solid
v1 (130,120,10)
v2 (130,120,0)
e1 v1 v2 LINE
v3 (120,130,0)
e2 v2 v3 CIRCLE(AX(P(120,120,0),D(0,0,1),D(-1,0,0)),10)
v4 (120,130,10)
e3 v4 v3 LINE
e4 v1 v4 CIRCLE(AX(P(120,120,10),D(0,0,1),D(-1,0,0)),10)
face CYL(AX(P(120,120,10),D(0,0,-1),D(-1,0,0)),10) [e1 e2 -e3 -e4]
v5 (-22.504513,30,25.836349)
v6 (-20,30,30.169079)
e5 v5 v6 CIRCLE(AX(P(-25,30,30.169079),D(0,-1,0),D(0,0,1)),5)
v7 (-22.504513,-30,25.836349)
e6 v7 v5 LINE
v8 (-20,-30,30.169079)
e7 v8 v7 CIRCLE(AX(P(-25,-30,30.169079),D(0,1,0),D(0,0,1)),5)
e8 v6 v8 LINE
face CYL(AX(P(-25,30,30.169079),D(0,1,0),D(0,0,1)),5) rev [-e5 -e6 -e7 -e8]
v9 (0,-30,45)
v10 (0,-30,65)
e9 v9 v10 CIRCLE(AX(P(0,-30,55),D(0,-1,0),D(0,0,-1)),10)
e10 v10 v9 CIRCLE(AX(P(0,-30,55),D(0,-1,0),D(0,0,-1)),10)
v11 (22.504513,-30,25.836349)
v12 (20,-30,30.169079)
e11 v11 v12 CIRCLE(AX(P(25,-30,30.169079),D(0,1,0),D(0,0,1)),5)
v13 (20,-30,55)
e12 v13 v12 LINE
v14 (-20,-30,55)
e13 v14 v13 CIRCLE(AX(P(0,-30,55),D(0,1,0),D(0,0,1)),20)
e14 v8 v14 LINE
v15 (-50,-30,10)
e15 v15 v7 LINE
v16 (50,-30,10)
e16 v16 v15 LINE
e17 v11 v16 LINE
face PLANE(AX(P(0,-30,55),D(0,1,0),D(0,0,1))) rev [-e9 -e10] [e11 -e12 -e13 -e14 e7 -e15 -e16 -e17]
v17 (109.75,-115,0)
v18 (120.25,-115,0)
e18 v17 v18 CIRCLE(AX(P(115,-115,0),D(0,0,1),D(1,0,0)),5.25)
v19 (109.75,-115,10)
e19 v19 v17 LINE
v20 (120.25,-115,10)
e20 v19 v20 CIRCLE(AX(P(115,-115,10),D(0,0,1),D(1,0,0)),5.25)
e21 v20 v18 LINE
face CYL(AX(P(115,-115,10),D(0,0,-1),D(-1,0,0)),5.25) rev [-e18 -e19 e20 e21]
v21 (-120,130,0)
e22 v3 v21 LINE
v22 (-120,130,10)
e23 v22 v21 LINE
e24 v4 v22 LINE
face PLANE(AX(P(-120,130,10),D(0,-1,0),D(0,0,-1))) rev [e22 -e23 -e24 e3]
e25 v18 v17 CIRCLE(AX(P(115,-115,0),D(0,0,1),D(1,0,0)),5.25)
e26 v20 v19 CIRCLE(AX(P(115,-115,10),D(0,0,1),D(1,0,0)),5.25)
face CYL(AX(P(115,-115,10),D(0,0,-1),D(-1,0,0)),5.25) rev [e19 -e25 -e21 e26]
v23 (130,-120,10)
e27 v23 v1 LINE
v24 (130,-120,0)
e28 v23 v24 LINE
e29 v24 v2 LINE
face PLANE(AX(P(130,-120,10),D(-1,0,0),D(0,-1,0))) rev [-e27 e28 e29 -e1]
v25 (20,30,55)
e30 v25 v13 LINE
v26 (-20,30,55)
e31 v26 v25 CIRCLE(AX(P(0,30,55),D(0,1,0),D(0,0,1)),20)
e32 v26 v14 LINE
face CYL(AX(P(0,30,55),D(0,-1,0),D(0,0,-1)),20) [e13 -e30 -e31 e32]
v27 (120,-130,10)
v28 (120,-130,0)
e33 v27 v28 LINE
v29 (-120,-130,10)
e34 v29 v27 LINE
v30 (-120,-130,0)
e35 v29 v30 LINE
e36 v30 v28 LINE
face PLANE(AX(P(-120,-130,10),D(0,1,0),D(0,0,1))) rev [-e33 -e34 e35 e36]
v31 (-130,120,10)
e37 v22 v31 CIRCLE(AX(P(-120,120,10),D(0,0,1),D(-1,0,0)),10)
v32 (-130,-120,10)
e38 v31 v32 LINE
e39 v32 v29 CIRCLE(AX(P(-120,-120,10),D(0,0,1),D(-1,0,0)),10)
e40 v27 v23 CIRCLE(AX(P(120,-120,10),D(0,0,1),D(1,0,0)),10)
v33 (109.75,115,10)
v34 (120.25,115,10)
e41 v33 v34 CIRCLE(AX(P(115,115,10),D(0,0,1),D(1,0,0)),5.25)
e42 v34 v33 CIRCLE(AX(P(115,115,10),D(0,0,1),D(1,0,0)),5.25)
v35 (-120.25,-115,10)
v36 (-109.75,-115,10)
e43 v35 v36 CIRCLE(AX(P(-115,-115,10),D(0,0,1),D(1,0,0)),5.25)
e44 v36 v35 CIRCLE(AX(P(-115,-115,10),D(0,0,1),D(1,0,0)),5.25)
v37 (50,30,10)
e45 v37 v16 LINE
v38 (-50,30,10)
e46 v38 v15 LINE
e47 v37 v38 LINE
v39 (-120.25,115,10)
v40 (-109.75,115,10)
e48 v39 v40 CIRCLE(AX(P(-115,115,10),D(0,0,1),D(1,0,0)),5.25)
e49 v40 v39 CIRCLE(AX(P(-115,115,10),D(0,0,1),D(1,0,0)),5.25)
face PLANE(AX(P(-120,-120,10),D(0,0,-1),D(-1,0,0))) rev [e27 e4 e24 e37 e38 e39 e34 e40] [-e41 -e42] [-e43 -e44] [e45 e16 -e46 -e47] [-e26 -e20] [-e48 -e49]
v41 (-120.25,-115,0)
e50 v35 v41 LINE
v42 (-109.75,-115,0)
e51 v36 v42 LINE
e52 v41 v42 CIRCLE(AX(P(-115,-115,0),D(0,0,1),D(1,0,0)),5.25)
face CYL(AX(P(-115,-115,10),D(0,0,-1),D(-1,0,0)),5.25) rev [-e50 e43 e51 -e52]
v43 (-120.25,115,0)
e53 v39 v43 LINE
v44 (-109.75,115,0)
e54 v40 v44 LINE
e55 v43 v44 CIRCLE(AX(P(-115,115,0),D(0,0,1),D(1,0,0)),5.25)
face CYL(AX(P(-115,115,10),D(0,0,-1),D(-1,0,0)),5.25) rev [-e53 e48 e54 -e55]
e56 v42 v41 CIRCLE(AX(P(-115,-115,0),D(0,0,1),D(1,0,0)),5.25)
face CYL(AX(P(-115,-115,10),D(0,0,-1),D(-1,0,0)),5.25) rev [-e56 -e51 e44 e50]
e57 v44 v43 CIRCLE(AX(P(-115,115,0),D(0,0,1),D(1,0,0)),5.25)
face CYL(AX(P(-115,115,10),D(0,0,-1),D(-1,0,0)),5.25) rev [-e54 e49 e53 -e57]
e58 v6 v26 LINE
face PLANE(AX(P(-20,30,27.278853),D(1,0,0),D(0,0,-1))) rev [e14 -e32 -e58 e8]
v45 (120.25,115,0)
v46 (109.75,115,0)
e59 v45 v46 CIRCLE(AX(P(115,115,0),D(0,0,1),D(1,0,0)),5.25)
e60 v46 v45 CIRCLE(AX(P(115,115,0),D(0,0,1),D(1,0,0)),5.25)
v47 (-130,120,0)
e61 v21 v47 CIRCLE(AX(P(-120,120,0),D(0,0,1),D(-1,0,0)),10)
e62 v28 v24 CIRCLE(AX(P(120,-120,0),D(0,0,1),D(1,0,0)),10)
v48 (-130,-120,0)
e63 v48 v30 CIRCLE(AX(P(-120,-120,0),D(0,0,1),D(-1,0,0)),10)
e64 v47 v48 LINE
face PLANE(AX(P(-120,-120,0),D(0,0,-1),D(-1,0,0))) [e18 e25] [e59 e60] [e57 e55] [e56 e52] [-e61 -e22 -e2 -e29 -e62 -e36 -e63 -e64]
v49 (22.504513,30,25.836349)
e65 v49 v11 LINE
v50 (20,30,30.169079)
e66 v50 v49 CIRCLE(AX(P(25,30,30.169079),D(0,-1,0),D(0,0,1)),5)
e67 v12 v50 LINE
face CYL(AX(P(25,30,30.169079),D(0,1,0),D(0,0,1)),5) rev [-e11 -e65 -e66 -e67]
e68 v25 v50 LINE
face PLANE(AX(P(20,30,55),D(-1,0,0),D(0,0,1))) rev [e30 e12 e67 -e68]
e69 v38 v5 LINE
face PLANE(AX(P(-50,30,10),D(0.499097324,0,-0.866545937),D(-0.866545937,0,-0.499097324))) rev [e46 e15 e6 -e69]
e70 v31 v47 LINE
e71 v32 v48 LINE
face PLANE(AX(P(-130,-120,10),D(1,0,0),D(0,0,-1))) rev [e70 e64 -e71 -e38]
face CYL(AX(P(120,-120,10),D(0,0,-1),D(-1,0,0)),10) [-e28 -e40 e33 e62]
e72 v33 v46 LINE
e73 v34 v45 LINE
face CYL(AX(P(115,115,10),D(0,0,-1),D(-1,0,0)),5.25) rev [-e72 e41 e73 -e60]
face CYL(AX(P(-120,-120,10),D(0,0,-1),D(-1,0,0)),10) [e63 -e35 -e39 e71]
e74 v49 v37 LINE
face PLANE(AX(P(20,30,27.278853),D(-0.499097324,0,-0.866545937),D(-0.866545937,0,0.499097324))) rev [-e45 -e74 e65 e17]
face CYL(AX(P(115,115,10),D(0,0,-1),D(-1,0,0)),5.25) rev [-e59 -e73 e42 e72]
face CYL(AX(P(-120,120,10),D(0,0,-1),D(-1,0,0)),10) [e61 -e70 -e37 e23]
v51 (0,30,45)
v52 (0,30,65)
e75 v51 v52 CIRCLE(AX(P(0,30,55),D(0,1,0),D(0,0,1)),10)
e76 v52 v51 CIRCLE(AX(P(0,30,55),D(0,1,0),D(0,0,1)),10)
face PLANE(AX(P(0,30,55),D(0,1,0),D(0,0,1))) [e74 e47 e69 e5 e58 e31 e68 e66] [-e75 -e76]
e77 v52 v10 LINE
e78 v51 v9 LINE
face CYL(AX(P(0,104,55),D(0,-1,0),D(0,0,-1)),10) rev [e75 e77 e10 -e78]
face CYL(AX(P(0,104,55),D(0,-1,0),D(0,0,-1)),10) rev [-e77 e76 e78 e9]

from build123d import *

# Parameters (mm, degrees)
SKETCH_1_R          = 5.25
EXTRUDE_1_DEPTH     = 10
EXTRUDE_2_DEPTH     = 30
SKETCH_3_R          = 10
CUT_EXTRUDE_1_DEPTH = 134
FILLET_1_R          = 5


with BuildPart() as part:
    # 草图1 → 凸台-拉伸1 (new body)
    with BuildSketch(Plane.XY):
        with BuildLine():
            Line((-120, -130), (120, -130))
            ThreePointArc((120, -130), (127.071067812, -127.071067812), (130, -120))
            Line((130, -120), (130, 120))
            ThreePointArc((130, 120), (127.071067812, 127.071067812), (120, 130))
            Line((120, 130), (-120, 130))
            ThreePointArc((-120, 130), (-127.071067812, 127.071067812), (-130, 120))
            Line((-130, 120), (-130, -120))
            ThreePointArc((-130, -120), (-127.071067812, -127.071067812), (-120, -130))
        make_face()
        with Locations((-115, 115)):
            Circle(SKETCH_1_R, mode=Mode.SUBTRACT)
        with Locations((115, 115)):
            Circle(SKETCH_1_R, mode=Mode.SUBTRACT)
        with Locations((115, -115)):
            Circle(SKETCH_1_R, mode=Mode.SUBTRACT)
        with Locations((-115, -115)):
            Circle(SKETCH_1_R, mode=Mode.SUBTRACT)
    extrude(amount=EXTRUDE_1_DEPTH)

    # 草图2 → 凸台-拉伸2 (add, symmetric)
    with BuildSketch(Plane(origin=(0, 0, 0), x_dir=(1, 0, 0), z_dir=(0, 1, 0))):
        with BuildLine():
            Line((-50, -10), (50, -10))
            Line((50, -10), (20, -27.278852826))
            Line((20, -27.278852826), (20, -55))
            ThreePointArc((20, -55), (0, -75), (-20, -55))
            Line((-20, -55), (-20, -27.278852826))
            Line((-20, -27.278852826), (-50, -10))
        make_face()
    extrude(amount=EXTRUDE_2_DEPTH, both=True)

    # 草图3 → 切除-拉伸1 (cut)
    with BuildSketch(Plane.XZ.offset(30)):
        with Locations(Location((0, 55, 0), (0, 0, 270))):
            Circle(SKETCH_3_R)
    extrude(amount=-CUT_EXTRUDE_1_DEPTH, mode=Mode.SUBTRACT)

    # 圆角1
    fillet_1_edges = [part.edges().sort_by_distance(p)[0] for p in [
        (-20, 0, 27.278852826),
        (20, 0, 27.278852826),
    ]]
    fillet(fillet_1_edges, radius=FILLET_1_R)


solid = part.part
